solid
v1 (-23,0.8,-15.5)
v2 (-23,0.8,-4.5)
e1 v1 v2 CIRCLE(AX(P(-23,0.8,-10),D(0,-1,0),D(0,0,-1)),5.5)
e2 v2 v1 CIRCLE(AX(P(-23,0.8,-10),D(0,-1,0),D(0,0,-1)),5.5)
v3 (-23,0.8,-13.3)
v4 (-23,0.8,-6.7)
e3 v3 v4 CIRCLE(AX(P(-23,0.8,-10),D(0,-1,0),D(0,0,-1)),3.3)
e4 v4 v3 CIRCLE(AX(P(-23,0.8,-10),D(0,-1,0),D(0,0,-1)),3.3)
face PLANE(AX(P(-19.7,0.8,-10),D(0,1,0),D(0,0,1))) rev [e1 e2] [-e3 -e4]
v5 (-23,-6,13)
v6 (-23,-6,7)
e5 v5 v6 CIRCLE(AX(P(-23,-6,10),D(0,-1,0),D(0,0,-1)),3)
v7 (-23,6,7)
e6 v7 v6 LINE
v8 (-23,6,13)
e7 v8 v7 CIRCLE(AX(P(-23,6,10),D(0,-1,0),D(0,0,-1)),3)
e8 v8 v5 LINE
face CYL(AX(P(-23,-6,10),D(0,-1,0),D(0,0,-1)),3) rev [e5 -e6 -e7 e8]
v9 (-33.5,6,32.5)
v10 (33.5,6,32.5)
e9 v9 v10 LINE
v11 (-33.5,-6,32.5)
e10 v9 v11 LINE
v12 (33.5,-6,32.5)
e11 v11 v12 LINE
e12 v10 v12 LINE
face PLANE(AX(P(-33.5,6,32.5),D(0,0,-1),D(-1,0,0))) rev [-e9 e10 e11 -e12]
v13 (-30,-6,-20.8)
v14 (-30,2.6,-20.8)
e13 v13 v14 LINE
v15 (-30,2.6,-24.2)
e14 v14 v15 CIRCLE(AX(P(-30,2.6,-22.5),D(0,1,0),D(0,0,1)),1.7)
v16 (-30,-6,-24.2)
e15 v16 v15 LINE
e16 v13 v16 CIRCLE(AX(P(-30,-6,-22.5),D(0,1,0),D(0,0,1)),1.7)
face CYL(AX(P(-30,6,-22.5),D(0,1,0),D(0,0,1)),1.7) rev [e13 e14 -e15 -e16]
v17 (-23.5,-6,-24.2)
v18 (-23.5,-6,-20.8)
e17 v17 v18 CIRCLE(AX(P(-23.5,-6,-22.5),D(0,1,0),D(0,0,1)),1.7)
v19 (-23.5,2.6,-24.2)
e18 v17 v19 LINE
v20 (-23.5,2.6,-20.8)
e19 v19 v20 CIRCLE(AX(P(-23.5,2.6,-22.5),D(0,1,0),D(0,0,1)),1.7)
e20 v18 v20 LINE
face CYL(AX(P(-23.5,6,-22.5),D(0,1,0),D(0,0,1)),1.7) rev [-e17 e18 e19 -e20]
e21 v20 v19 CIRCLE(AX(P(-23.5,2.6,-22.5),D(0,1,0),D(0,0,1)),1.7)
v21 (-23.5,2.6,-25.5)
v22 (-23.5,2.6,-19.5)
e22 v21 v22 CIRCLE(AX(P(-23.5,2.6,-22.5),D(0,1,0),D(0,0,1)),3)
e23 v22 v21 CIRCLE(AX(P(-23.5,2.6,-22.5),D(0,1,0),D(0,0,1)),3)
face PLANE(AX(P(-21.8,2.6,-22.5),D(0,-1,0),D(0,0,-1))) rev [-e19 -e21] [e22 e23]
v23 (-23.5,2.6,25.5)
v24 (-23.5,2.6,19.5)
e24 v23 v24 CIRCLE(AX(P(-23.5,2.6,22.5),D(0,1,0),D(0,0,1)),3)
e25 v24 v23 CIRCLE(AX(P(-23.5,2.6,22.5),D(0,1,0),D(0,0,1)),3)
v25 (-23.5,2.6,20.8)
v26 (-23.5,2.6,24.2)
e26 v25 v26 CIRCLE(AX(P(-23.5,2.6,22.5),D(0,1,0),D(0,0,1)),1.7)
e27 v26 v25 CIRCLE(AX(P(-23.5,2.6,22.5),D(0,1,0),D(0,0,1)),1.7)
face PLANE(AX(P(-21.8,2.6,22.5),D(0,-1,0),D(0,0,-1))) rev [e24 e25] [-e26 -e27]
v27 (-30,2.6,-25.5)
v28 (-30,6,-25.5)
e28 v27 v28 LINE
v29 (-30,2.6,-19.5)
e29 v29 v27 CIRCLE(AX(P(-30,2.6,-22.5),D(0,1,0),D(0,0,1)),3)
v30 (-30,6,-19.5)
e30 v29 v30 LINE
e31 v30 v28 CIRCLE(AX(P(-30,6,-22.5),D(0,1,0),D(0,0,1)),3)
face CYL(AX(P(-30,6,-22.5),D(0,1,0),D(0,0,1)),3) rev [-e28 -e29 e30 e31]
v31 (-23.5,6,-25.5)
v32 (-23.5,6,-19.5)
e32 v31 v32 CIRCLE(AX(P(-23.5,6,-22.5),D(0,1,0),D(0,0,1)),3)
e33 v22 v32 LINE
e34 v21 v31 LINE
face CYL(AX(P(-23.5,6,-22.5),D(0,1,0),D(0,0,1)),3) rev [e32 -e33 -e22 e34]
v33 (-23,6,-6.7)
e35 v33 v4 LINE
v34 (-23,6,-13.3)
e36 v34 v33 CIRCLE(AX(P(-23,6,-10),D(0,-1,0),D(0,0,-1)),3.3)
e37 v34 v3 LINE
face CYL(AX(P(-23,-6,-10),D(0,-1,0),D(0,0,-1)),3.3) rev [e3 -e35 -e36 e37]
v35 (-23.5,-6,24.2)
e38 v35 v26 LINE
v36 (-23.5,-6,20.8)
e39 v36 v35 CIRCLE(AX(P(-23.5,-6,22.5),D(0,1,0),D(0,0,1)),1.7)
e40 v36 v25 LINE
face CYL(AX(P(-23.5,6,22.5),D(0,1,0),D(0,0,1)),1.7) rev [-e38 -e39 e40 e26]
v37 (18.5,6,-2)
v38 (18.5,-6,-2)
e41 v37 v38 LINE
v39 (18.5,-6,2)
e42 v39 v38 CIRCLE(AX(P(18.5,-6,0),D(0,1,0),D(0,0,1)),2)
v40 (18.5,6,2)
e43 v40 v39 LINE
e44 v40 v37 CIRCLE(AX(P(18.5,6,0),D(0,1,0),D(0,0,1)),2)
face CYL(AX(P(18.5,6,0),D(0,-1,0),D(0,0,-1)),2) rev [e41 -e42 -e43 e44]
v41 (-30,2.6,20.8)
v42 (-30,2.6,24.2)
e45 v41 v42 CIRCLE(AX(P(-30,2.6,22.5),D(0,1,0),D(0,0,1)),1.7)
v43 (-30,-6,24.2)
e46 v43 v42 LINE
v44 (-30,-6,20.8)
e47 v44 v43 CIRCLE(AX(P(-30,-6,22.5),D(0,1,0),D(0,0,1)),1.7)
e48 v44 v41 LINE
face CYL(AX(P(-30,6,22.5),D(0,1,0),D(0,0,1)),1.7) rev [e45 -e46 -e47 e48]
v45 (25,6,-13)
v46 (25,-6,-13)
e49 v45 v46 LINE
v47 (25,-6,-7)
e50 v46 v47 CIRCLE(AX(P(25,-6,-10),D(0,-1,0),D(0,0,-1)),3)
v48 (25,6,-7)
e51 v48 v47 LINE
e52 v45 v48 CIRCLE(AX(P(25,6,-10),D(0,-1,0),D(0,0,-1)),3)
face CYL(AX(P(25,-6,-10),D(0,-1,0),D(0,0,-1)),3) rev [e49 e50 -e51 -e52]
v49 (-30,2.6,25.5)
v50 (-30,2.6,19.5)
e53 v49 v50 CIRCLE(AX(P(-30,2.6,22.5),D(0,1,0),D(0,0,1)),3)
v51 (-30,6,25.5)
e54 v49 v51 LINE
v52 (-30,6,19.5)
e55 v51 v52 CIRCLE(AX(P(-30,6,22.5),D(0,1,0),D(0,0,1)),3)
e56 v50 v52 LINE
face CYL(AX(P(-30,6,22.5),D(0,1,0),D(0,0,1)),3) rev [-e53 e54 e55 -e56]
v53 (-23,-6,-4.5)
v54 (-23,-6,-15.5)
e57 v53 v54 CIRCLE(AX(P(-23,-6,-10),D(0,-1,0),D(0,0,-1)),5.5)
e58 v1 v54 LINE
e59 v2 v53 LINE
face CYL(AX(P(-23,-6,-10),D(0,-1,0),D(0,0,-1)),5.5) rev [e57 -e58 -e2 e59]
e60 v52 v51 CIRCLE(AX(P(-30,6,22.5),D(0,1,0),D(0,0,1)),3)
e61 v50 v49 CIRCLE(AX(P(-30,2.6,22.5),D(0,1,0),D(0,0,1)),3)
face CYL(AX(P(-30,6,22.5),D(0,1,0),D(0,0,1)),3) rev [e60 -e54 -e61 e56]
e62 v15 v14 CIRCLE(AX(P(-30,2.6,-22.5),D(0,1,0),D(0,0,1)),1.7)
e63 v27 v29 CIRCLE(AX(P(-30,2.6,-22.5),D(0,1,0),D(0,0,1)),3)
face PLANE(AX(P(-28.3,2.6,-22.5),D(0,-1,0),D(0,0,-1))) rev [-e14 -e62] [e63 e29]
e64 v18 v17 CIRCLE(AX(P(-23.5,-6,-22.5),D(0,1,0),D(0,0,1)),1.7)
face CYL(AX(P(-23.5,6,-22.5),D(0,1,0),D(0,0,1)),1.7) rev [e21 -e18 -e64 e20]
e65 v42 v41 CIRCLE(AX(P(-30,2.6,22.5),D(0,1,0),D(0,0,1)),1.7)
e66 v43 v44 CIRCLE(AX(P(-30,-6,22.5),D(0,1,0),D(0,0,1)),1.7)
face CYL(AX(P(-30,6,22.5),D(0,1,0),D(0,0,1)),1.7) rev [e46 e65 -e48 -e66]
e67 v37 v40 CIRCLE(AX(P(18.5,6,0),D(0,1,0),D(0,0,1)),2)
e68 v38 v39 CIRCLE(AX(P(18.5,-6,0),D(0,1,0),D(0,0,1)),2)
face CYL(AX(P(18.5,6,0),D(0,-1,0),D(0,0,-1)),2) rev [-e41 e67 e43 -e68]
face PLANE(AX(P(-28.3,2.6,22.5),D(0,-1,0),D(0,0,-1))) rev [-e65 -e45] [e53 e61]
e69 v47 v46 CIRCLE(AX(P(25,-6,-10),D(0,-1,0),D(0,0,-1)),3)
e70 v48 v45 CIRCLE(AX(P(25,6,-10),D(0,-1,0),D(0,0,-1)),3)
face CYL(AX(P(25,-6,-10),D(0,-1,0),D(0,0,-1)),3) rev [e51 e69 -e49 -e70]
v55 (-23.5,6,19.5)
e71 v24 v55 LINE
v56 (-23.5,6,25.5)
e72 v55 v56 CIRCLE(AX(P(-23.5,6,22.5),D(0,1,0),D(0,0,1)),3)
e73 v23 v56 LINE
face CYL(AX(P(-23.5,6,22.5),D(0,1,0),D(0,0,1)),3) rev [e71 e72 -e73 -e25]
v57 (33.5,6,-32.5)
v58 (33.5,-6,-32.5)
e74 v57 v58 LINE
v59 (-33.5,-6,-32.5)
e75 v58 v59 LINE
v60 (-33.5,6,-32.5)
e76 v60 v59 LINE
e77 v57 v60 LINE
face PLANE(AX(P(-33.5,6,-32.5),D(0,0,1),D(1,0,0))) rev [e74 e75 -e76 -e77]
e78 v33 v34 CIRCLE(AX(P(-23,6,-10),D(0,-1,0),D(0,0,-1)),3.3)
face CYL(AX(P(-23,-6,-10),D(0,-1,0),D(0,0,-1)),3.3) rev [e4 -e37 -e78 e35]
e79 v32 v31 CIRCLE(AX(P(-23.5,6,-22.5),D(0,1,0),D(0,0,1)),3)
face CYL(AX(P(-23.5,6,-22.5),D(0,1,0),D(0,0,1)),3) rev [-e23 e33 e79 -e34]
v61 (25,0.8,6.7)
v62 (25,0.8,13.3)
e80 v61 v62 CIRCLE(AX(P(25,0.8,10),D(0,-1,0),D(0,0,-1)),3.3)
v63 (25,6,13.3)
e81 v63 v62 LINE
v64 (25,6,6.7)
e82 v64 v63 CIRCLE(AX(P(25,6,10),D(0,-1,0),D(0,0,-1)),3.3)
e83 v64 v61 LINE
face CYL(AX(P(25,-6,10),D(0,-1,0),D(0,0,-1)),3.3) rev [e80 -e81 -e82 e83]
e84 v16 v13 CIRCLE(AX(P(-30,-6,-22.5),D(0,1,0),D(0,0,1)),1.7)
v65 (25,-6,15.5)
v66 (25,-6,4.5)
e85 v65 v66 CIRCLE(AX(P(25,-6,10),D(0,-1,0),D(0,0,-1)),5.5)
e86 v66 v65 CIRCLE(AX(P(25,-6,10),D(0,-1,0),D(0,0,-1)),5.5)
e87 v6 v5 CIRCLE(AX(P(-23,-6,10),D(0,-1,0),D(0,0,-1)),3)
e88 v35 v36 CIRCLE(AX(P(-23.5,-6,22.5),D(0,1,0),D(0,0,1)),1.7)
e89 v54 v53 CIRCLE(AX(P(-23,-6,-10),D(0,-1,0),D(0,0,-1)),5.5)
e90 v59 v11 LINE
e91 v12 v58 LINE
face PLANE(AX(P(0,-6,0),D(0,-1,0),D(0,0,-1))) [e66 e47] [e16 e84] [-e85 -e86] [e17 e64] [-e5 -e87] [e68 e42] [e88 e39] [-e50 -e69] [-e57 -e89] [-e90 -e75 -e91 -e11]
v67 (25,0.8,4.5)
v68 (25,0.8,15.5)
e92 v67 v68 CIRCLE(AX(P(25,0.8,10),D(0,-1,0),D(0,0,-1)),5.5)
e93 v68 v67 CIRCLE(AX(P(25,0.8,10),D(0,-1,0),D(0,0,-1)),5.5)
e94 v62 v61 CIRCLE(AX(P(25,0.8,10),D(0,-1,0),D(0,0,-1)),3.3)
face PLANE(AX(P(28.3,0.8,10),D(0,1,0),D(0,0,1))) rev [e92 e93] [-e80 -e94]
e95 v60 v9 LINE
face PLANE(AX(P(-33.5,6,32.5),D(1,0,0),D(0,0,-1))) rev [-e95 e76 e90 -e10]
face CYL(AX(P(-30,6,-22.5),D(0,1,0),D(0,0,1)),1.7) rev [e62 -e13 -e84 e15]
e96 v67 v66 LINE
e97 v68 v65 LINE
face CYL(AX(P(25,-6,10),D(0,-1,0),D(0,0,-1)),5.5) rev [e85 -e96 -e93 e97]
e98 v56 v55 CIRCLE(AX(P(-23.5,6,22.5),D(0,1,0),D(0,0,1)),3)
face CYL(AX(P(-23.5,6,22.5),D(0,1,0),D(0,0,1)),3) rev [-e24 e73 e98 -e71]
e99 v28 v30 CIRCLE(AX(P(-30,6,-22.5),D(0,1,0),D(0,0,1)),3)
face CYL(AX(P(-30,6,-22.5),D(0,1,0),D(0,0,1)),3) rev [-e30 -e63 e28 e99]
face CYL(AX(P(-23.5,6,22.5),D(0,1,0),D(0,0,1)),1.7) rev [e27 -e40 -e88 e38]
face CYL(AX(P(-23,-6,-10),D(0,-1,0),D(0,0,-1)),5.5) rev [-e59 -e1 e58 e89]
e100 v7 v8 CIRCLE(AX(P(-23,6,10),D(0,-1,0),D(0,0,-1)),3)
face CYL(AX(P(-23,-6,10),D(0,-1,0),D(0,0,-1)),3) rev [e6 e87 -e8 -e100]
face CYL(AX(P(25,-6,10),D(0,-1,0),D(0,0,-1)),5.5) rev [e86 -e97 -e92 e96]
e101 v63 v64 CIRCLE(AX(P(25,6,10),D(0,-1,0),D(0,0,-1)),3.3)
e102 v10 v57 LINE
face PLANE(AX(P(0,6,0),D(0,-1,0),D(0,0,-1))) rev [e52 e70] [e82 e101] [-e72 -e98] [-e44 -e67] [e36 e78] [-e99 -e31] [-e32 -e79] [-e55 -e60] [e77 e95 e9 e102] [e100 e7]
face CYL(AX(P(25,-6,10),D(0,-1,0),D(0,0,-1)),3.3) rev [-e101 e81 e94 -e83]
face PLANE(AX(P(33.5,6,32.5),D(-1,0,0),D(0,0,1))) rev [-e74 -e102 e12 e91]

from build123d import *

# Parameters (mm, degrees)
SKETCH_1_W                   = 67
SKETCH_1_H                   = 65
SKETCH_1_R                   = 2
EXTRUDE_1_DEPTH              = 6
HOLE_WIZARD_M3_1_D           = 3.4
HOLE_WIZARD_M3_1_CBORE_D     = 6
HOLE_WIZARD_M3_1_CBORE_DEPTH = 3.4
HOLE_WIZARD_M6_1_D           = 6.6
HOLE_WIZARD_M6_1_CBORE_D     = 11
HOLE_WIZARD_M6_1_CBORE_DEPTH = 6.8
F_6_0MM_1_D                  = 6


with BuildPart() as part:
    # 草图1 → 凸台-拉伸1 (new, symmetric)
    with BuildSketch(Plane(origin=(0, 0, 0), x_dir=(1, 0, 0), z_dir=(0, 1, 0))):
        Rectangle(SKETCH_1_W, SKETCH_1_H)
        with Locations(Location((18.5, 0, 0), (0, 0, 270))):
            Circle(SKETCH_1_R, mode=Mode.SUBTRACT)
    extrude(amount=EXTRUDE_1_DEPTH, both=True)

    # M3 六角圆柱头螺钉的柱形沉头孔1 (through all)
    with Locations(Plane(origin=(0, 6, 0), x_dir=(1, 0, 0), z_dir=(0, 1, 0))):
        with Locations((-30, -22.5), (-30, -37.5), (-23.5, -37.5), (-23.5, -22.5), (-23.5, 22.5), (-23.5, 37.5), (-30, 37.5), (-30, 22.5)):
            CounterBoreHole(HOLE_WIZARD_M3_1_D / 2, HOLE_WIZARD_M3_1_CBORE_D / 2, HOLE_WIZARD_M3_1_CBORE_DEPTH)

    # M6 六角圆柱头螺钉的柱形沉头孔1 (through all)
    with Locations(Plane.XZ.offset(6)):
        with Locations((-23, -10), (25, 10)):
            CounterBoreHole(HOLE_WIZARD_M6_1_D / 2, HOLE_WIZARD_M6_1_CBORE_D / 2, HOLE_WIZARD_M6_1_CBORE_DEPTH)

    # Ø6.0mm 暗销孔1 (through all)
    with Locations(Plane(origin=(0, -6, 0), x_dir=(-1, 0, 0), z_dir=(0, -1, 0))):
        with Locations((-25, 10), (23, -10)):
            Hole(F_6_0MM_1_D / 2)


solid = part.part
